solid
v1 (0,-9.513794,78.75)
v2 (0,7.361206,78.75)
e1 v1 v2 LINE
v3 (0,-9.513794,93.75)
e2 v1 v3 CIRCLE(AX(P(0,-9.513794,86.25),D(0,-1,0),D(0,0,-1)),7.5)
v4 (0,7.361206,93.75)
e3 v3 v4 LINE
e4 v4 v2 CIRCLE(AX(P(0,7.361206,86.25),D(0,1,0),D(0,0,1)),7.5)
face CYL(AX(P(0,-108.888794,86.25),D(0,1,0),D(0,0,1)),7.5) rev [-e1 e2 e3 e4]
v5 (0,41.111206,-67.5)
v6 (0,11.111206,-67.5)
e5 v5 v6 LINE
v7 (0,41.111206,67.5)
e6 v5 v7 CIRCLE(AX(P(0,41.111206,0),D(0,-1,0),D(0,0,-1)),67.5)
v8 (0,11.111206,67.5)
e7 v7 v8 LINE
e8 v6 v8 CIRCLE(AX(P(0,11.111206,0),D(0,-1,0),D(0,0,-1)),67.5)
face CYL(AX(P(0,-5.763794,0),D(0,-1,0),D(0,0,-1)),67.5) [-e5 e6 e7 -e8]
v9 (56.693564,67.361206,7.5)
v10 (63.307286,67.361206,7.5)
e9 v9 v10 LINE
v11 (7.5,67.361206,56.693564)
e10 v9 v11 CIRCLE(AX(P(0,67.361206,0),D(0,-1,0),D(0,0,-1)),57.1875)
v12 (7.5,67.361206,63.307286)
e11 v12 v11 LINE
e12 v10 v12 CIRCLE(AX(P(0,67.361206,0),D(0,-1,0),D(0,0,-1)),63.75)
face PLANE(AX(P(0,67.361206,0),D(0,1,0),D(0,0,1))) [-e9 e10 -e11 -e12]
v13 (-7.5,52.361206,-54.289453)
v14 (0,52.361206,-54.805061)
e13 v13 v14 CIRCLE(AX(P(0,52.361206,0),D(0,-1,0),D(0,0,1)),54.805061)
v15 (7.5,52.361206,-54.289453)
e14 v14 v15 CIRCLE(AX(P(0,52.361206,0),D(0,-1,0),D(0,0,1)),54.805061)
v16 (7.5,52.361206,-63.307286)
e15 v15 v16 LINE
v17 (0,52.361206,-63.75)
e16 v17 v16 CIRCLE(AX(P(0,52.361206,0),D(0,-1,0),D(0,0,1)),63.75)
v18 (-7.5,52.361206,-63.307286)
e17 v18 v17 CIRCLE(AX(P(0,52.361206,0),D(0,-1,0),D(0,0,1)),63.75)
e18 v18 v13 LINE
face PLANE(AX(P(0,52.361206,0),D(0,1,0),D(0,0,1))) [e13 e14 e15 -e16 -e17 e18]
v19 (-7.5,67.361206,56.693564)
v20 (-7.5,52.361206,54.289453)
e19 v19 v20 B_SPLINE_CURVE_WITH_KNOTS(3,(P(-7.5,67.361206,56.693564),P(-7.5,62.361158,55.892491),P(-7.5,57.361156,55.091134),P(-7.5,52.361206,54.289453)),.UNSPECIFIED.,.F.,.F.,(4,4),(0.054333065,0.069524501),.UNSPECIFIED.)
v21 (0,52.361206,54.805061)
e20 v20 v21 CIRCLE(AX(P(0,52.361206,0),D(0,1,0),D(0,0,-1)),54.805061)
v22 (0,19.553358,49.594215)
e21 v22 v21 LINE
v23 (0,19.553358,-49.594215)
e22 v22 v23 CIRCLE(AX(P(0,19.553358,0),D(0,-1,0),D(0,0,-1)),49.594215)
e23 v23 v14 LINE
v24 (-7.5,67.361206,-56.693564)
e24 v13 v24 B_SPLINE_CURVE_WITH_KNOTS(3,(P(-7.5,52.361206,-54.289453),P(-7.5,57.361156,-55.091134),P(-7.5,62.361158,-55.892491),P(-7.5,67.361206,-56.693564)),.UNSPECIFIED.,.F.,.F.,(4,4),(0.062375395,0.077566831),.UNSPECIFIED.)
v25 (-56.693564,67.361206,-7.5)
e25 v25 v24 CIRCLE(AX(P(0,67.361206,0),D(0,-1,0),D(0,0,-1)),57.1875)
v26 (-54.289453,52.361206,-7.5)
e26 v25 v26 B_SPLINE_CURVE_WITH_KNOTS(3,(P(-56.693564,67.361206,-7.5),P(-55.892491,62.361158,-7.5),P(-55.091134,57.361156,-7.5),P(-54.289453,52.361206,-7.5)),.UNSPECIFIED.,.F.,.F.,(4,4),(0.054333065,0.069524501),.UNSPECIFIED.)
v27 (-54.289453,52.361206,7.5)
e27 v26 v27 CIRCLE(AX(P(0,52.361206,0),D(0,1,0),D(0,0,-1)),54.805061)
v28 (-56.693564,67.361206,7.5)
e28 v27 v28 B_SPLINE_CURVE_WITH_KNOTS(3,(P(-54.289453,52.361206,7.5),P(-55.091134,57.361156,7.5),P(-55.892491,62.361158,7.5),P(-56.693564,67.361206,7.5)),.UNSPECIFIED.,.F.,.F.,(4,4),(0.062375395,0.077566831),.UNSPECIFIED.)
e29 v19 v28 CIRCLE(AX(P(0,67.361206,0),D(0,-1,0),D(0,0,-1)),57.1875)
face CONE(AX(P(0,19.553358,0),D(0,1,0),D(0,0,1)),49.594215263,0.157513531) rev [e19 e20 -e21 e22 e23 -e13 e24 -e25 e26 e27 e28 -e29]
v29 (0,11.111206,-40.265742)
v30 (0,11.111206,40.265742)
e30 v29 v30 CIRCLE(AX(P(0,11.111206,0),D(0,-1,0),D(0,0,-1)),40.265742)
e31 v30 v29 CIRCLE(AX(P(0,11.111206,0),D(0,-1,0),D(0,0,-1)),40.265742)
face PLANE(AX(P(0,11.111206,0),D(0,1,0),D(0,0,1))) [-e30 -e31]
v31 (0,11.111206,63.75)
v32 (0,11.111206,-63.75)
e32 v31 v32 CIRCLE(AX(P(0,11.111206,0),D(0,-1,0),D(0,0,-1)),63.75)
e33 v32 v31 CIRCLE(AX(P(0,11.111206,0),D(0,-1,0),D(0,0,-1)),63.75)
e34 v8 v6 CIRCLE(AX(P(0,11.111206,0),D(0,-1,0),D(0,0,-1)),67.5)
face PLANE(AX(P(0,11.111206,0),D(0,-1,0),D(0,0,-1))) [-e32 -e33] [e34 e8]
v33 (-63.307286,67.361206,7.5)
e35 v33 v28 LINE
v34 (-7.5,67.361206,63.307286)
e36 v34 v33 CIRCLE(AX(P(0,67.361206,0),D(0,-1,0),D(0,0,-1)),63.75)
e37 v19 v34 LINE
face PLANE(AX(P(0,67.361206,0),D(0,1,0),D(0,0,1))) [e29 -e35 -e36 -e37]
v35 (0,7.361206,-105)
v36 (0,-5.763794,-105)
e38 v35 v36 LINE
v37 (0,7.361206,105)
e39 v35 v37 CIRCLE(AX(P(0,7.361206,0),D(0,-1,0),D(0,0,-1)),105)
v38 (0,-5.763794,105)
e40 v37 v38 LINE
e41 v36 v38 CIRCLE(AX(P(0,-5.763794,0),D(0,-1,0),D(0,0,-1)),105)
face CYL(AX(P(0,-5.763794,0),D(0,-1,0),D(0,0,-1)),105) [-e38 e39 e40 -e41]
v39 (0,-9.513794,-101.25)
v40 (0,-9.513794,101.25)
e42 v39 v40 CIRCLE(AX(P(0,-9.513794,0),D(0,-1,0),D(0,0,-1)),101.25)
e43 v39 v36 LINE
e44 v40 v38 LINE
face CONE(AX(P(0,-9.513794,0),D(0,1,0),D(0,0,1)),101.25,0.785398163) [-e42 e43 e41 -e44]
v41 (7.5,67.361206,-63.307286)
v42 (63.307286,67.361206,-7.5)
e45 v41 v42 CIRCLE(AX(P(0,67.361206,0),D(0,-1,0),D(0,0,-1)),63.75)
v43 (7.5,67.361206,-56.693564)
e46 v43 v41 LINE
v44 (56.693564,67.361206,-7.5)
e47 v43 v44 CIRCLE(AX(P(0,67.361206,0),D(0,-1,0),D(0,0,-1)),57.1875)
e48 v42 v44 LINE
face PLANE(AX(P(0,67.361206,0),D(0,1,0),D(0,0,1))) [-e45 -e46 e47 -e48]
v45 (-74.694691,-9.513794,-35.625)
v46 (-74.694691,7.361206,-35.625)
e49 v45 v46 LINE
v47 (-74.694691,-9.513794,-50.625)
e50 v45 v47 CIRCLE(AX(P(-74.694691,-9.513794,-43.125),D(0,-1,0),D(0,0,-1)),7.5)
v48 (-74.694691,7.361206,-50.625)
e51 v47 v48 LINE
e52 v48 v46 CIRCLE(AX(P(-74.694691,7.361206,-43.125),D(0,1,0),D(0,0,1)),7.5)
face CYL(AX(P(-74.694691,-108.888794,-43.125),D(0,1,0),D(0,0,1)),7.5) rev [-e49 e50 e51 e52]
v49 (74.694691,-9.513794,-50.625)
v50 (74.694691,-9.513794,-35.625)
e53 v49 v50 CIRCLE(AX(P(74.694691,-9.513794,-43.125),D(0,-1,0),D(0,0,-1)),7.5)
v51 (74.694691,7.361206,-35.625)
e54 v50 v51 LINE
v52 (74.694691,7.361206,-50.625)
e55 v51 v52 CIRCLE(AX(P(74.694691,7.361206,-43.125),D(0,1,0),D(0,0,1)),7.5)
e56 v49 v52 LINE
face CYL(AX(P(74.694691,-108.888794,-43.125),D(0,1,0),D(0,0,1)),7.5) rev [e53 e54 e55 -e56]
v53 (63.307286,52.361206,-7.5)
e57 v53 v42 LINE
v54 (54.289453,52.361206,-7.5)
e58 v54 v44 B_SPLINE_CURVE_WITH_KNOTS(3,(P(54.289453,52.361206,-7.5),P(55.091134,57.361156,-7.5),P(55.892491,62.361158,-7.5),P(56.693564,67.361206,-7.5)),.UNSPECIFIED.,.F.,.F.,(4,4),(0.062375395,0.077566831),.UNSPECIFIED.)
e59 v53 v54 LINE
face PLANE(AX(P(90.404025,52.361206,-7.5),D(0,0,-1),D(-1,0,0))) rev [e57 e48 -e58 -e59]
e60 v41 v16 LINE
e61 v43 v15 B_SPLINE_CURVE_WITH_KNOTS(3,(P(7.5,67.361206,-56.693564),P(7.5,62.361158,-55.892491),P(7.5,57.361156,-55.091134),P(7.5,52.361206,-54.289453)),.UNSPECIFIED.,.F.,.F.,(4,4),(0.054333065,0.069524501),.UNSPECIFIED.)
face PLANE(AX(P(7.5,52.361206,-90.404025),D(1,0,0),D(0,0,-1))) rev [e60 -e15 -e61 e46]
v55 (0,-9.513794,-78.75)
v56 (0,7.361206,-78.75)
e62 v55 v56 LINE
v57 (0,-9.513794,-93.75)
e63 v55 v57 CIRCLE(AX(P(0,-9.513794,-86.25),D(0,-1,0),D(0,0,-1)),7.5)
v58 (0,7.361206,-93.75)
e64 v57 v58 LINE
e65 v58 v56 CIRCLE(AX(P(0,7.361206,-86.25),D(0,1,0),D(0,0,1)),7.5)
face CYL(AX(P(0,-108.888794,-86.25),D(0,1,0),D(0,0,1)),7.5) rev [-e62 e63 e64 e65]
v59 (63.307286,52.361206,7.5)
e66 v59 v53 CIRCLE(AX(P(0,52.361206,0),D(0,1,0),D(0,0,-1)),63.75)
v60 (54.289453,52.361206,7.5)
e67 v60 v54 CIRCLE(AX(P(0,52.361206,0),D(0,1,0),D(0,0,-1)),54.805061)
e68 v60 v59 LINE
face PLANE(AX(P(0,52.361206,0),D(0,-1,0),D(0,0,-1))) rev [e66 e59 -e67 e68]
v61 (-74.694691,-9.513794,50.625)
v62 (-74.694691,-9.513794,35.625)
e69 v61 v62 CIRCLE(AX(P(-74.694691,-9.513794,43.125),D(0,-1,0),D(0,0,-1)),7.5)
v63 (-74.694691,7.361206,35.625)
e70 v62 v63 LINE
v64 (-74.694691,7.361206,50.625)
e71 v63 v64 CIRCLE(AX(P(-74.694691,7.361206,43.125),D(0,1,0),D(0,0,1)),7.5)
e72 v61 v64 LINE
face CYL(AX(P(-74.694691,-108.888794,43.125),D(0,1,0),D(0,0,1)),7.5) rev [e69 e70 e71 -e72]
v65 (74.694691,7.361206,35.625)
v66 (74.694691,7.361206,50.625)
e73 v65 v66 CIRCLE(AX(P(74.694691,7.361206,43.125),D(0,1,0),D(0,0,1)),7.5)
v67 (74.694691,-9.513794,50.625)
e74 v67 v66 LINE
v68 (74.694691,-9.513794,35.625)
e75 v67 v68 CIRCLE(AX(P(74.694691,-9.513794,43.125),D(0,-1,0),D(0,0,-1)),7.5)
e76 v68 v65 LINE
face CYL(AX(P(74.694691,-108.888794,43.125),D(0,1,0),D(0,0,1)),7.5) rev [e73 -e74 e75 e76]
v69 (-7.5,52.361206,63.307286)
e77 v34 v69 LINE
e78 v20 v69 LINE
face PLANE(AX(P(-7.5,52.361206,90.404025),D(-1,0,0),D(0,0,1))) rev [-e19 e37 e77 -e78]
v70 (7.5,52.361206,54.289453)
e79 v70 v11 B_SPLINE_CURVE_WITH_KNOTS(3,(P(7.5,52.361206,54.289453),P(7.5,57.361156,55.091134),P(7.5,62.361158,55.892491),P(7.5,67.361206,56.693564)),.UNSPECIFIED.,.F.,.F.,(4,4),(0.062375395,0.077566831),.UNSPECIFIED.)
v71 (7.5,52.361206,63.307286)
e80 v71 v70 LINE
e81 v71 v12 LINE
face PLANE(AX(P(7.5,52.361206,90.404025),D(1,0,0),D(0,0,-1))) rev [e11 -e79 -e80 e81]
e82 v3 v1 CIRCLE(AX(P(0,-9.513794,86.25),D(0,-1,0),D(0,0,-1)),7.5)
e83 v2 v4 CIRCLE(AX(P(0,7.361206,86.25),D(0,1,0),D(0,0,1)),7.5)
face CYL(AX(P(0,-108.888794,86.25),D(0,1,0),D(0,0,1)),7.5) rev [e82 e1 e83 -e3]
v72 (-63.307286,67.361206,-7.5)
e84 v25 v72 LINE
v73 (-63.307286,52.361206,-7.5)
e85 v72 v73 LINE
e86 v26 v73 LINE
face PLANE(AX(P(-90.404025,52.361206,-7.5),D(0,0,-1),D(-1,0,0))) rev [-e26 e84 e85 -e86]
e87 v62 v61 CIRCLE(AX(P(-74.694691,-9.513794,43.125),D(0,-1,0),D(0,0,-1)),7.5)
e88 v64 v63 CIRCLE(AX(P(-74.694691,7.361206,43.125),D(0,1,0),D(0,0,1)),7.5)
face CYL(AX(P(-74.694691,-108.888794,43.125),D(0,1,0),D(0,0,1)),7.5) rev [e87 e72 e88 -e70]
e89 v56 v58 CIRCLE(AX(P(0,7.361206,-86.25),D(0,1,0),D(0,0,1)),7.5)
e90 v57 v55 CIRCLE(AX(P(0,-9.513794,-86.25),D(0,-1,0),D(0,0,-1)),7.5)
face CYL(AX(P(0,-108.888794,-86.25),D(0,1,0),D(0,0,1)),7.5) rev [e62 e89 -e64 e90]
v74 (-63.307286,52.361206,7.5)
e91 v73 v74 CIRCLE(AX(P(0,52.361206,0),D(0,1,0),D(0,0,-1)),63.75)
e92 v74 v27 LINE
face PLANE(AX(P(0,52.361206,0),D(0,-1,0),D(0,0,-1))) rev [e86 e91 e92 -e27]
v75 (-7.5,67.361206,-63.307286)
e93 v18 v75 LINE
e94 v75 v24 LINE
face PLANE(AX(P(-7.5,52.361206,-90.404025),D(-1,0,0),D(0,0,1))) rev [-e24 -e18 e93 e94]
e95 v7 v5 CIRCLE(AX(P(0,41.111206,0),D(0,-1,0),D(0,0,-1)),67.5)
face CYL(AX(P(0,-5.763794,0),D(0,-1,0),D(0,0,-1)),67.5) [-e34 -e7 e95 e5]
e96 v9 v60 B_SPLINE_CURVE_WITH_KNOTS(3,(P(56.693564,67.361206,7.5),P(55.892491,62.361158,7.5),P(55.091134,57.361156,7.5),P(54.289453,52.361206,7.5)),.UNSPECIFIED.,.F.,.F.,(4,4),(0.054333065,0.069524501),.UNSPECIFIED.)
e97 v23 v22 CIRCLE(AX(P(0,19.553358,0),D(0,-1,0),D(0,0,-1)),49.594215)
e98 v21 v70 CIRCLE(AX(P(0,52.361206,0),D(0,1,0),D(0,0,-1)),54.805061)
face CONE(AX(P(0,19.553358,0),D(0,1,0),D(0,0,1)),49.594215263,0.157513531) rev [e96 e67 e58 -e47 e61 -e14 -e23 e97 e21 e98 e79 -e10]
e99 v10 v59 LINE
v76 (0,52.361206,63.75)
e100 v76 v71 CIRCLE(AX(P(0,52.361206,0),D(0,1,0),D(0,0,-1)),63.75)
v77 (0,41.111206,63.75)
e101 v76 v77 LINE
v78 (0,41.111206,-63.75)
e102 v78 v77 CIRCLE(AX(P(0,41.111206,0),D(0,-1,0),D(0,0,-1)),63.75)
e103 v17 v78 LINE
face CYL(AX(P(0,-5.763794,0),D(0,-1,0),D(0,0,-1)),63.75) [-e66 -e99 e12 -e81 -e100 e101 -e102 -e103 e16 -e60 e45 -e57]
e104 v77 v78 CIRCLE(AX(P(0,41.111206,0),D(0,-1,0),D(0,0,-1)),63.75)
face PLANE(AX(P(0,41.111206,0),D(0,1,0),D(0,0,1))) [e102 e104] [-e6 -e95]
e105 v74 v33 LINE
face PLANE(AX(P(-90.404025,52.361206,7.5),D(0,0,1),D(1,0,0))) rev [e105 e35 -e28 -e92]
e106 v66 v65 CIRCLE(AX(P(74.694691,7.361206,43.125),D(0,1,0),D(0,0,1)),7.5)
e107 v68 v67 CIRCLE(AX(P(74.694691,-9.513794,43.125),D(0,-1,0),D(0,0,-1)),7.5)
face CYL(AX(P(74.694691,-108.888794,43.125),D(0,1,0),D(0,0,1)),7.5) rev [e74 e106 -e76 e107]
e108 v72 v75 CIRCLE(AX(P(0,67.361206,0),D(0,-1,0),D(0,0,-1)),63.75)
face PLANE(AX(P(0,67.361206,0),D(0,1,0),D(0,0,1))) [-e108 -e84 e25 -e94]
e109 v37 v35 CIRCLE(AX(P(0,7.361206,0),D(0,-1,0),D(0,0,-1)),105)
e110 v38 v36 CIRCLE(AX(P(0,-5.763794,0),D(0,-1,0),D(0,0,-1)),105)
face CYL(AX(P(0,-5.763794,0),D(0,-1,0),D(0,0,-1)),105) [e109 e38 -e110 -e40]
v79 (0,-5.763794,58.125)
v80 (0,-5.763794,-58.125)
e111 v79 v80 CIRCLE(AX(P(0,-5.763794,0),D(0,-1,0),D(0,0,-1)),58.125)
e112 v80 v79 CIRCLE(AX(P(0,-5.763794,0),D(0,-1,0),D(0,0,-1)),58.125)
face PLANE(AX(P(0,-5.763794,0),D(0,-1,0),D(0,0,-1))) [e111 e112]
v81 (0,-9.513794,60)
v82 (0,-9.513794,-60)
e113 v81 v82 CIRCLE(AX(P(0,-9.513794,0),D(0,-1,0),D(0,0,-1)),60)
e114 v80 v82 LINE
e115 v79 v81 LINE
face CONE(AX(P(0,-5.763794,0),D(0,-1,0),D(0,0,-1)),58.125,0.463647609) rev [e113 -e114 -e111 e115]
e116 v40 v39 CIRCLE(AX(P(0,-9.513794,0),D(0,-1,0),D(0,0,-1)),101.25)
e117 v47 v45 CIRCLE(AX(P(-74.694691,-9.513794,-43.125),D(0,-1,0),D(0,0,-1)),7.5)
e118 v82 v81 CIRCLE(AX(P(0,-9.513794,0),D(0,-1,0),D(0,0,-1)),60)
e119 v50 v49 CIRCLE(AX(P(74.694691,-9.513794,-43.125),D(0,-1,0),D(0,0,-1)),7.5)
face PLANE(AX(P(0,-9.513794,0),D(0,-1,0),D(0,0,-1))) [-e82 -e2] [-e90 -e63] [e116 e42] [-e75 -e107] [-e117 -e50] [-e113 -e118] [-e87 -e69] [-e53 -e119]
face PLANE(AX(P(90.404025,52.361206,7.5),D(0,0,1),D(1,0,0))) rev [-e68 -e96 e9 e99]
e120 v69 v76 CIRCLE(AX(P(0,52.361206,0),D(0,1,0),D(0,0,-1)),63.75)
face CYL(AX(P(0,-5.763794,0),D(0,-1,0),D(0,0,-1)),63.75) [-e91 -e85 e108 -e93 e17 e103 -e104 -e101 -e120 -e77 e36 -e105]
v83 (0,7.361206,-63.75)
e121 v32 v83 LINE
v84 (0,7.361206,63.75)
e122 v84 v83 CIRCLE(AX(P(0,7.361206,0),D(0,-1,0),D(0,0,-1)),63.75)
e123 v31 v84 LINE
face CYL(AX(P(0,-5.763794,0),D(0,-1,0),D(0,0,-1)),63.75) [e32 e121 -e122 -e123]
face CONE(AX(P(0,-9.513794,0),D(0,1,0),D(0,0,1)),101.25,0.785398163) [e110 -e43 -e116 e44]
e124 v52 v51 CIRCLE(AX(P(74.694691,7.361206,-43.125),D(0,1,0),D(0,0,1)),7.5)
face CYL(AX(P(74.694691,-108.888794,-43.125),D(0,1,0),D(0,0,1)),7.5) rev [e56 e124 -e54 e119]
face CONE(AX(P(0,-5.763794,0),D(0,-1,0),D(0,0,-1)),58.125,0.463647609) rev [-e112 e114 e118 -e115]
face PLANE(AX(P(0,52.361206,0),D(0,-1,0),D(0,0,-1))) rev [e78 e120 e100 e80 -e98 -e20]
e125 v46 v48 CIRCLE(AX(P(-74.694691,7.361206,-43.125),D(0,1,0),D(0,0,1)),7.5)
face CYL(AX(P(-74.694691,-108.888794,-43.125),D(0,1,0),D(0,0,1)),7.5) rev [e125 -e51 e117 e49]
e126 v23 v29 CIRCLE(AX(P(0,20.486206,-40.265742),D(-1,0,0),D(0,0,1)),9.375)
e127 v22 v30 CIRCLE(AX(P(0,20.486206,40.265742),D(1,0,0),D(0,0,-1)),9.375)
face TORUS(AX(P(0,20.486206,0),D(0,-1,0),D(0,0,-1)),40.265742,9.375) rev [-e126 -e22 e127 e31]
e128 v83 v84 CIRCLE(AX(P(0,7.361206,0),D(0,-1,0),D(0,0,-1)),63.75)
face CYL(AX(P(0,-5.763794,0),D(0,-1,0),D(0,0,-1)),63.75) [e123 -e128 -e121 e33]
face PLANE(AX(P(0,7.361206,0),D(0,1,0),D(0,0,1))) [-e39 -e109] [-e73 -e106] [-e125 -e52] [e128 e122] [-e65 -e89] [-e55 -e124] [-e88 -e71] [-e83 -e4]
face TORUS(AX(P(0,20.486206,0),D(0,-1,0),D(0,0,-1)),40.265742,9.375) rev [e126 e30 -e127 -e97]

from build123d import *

# Parameters (mm, degrees)
SKETCH2_W          = 33.532576539
SKETCH2_H          = 8
SKETCH2_W_2        = 8
SKETCH2_H_2        = 33.532576539
CUT_EXTRUDE1_DEPTH = 8
SKETCH3_R          = 4
CUT_EXTRUDE2_DEPTH = 94
SCALE_1_SCALE      = 1.875


with BuildPart() as part:
    # Sketch1 → Revolve1 (revolve)
    with BuildSketch(Plane.XY, mode=Mode.PRIVATE) as revolve1_sk:
        with BuildLine():
            Line((0, 11), (0, 2))
            Line((0, 2), (31, 2))
            Line((31, 2), (32, 0))
            Line((32, 0), (54, 0))
            Line((54, 0), (56, 2))
            Line((56, 2), (56, 9))
            Line((56, 9), (34, 9))
            Line((34, 9), (34, 11))
            Line((34, 11), (36, 11))
            Line((36, 11), (36, 27))
            Line((36, 27), (34, 27))
            Line((34, 27), (34, 41))
            Line((34, 41), (30.5, 41))
            Line((30.5, 41), (26.45024814, 15.502481405))
            ThreePointArc((26.45024814, 15.502481405), (24.830088793, 12.292737332), (21.475062189, 11))
            Line((21.475062189, 11), (16.570568921, 11))
            Line((16.570568921, 11), (0, 11))
        make_face()
    revolve(revolve1_sk.sketch.rotate(Axis((0, 2, 0), (0, 1, 0)), 90), axis=Axis((0, 2, 0), (0, 1, 0)))

    # Sketch2 → Cut-Extrude1 (cut)
    with BuildSketch(Plane(origin=(0, 41, 0), x_dir=(1, 0, 0), z_dir=(0, 1, 0))):
        with Locations((31.449191607, 0)):
            Rectangle(SKETCH2_W, SKETCH2_H)
        with Locations((0, 31.449191607)):
            Rectangle(SKETCH2_W_2, SKETCH2_H_2)
        with Locations((0, -31.449191607)):
            Rectangle(SKETCH2_W_2, SKETCH2_H_2)
        with Locations((-31.449191607, 0)):
            Rectangle(SKETCH2_W, SKETCH2_H)
    extrude(amount=-CUT_EXTRUDE1_DEPTH, mode=Mode.SUBTRACT)

    # Sketch3 → Cut-Extrude2 (cut)
    with BuildSketch(Plane(origin=(0, 41, 0), x_dir=(1, 0, 0), z_dir=(0, 1, 0))):
        with Locations(Location((-39.837168574, -23, 0), (0, 0, 270))):
            Circle(SKETCH3_R)
        with Locations(Location((0, 46, 0), (0, 0, 270))):
            Circle(SKETCH3_R)
        with Locations(Location((39.837168574, 23, 0), (0, 0, 270))):
            Circle(SKETCH3_R)
        with Locations(Location((-39.837168574, 23, 0), (0, 0, 270))):
            Circle(SKETCH3_R)
        with Locations(Location((0, -46, 0), (0, 0, 270))):
            Circle(SKETCH3_R)
        with Locations(Location((39.837168574, -23, 0), (0, 0, 270))):
            Circle(SKETCH3_R)
    extrude(amount=-CUT_EXTRUDE2_DEPTH, mode=Mode.SUBTRACT)


with BuildPart() as part_1:
    # Scale 1: scaled about (0, 10.8729077, 0)
    add(part.part.scale(SCALE_1_SCALE).moved(Location((0, -9.513794238, 0))))


solid = part_1.part
